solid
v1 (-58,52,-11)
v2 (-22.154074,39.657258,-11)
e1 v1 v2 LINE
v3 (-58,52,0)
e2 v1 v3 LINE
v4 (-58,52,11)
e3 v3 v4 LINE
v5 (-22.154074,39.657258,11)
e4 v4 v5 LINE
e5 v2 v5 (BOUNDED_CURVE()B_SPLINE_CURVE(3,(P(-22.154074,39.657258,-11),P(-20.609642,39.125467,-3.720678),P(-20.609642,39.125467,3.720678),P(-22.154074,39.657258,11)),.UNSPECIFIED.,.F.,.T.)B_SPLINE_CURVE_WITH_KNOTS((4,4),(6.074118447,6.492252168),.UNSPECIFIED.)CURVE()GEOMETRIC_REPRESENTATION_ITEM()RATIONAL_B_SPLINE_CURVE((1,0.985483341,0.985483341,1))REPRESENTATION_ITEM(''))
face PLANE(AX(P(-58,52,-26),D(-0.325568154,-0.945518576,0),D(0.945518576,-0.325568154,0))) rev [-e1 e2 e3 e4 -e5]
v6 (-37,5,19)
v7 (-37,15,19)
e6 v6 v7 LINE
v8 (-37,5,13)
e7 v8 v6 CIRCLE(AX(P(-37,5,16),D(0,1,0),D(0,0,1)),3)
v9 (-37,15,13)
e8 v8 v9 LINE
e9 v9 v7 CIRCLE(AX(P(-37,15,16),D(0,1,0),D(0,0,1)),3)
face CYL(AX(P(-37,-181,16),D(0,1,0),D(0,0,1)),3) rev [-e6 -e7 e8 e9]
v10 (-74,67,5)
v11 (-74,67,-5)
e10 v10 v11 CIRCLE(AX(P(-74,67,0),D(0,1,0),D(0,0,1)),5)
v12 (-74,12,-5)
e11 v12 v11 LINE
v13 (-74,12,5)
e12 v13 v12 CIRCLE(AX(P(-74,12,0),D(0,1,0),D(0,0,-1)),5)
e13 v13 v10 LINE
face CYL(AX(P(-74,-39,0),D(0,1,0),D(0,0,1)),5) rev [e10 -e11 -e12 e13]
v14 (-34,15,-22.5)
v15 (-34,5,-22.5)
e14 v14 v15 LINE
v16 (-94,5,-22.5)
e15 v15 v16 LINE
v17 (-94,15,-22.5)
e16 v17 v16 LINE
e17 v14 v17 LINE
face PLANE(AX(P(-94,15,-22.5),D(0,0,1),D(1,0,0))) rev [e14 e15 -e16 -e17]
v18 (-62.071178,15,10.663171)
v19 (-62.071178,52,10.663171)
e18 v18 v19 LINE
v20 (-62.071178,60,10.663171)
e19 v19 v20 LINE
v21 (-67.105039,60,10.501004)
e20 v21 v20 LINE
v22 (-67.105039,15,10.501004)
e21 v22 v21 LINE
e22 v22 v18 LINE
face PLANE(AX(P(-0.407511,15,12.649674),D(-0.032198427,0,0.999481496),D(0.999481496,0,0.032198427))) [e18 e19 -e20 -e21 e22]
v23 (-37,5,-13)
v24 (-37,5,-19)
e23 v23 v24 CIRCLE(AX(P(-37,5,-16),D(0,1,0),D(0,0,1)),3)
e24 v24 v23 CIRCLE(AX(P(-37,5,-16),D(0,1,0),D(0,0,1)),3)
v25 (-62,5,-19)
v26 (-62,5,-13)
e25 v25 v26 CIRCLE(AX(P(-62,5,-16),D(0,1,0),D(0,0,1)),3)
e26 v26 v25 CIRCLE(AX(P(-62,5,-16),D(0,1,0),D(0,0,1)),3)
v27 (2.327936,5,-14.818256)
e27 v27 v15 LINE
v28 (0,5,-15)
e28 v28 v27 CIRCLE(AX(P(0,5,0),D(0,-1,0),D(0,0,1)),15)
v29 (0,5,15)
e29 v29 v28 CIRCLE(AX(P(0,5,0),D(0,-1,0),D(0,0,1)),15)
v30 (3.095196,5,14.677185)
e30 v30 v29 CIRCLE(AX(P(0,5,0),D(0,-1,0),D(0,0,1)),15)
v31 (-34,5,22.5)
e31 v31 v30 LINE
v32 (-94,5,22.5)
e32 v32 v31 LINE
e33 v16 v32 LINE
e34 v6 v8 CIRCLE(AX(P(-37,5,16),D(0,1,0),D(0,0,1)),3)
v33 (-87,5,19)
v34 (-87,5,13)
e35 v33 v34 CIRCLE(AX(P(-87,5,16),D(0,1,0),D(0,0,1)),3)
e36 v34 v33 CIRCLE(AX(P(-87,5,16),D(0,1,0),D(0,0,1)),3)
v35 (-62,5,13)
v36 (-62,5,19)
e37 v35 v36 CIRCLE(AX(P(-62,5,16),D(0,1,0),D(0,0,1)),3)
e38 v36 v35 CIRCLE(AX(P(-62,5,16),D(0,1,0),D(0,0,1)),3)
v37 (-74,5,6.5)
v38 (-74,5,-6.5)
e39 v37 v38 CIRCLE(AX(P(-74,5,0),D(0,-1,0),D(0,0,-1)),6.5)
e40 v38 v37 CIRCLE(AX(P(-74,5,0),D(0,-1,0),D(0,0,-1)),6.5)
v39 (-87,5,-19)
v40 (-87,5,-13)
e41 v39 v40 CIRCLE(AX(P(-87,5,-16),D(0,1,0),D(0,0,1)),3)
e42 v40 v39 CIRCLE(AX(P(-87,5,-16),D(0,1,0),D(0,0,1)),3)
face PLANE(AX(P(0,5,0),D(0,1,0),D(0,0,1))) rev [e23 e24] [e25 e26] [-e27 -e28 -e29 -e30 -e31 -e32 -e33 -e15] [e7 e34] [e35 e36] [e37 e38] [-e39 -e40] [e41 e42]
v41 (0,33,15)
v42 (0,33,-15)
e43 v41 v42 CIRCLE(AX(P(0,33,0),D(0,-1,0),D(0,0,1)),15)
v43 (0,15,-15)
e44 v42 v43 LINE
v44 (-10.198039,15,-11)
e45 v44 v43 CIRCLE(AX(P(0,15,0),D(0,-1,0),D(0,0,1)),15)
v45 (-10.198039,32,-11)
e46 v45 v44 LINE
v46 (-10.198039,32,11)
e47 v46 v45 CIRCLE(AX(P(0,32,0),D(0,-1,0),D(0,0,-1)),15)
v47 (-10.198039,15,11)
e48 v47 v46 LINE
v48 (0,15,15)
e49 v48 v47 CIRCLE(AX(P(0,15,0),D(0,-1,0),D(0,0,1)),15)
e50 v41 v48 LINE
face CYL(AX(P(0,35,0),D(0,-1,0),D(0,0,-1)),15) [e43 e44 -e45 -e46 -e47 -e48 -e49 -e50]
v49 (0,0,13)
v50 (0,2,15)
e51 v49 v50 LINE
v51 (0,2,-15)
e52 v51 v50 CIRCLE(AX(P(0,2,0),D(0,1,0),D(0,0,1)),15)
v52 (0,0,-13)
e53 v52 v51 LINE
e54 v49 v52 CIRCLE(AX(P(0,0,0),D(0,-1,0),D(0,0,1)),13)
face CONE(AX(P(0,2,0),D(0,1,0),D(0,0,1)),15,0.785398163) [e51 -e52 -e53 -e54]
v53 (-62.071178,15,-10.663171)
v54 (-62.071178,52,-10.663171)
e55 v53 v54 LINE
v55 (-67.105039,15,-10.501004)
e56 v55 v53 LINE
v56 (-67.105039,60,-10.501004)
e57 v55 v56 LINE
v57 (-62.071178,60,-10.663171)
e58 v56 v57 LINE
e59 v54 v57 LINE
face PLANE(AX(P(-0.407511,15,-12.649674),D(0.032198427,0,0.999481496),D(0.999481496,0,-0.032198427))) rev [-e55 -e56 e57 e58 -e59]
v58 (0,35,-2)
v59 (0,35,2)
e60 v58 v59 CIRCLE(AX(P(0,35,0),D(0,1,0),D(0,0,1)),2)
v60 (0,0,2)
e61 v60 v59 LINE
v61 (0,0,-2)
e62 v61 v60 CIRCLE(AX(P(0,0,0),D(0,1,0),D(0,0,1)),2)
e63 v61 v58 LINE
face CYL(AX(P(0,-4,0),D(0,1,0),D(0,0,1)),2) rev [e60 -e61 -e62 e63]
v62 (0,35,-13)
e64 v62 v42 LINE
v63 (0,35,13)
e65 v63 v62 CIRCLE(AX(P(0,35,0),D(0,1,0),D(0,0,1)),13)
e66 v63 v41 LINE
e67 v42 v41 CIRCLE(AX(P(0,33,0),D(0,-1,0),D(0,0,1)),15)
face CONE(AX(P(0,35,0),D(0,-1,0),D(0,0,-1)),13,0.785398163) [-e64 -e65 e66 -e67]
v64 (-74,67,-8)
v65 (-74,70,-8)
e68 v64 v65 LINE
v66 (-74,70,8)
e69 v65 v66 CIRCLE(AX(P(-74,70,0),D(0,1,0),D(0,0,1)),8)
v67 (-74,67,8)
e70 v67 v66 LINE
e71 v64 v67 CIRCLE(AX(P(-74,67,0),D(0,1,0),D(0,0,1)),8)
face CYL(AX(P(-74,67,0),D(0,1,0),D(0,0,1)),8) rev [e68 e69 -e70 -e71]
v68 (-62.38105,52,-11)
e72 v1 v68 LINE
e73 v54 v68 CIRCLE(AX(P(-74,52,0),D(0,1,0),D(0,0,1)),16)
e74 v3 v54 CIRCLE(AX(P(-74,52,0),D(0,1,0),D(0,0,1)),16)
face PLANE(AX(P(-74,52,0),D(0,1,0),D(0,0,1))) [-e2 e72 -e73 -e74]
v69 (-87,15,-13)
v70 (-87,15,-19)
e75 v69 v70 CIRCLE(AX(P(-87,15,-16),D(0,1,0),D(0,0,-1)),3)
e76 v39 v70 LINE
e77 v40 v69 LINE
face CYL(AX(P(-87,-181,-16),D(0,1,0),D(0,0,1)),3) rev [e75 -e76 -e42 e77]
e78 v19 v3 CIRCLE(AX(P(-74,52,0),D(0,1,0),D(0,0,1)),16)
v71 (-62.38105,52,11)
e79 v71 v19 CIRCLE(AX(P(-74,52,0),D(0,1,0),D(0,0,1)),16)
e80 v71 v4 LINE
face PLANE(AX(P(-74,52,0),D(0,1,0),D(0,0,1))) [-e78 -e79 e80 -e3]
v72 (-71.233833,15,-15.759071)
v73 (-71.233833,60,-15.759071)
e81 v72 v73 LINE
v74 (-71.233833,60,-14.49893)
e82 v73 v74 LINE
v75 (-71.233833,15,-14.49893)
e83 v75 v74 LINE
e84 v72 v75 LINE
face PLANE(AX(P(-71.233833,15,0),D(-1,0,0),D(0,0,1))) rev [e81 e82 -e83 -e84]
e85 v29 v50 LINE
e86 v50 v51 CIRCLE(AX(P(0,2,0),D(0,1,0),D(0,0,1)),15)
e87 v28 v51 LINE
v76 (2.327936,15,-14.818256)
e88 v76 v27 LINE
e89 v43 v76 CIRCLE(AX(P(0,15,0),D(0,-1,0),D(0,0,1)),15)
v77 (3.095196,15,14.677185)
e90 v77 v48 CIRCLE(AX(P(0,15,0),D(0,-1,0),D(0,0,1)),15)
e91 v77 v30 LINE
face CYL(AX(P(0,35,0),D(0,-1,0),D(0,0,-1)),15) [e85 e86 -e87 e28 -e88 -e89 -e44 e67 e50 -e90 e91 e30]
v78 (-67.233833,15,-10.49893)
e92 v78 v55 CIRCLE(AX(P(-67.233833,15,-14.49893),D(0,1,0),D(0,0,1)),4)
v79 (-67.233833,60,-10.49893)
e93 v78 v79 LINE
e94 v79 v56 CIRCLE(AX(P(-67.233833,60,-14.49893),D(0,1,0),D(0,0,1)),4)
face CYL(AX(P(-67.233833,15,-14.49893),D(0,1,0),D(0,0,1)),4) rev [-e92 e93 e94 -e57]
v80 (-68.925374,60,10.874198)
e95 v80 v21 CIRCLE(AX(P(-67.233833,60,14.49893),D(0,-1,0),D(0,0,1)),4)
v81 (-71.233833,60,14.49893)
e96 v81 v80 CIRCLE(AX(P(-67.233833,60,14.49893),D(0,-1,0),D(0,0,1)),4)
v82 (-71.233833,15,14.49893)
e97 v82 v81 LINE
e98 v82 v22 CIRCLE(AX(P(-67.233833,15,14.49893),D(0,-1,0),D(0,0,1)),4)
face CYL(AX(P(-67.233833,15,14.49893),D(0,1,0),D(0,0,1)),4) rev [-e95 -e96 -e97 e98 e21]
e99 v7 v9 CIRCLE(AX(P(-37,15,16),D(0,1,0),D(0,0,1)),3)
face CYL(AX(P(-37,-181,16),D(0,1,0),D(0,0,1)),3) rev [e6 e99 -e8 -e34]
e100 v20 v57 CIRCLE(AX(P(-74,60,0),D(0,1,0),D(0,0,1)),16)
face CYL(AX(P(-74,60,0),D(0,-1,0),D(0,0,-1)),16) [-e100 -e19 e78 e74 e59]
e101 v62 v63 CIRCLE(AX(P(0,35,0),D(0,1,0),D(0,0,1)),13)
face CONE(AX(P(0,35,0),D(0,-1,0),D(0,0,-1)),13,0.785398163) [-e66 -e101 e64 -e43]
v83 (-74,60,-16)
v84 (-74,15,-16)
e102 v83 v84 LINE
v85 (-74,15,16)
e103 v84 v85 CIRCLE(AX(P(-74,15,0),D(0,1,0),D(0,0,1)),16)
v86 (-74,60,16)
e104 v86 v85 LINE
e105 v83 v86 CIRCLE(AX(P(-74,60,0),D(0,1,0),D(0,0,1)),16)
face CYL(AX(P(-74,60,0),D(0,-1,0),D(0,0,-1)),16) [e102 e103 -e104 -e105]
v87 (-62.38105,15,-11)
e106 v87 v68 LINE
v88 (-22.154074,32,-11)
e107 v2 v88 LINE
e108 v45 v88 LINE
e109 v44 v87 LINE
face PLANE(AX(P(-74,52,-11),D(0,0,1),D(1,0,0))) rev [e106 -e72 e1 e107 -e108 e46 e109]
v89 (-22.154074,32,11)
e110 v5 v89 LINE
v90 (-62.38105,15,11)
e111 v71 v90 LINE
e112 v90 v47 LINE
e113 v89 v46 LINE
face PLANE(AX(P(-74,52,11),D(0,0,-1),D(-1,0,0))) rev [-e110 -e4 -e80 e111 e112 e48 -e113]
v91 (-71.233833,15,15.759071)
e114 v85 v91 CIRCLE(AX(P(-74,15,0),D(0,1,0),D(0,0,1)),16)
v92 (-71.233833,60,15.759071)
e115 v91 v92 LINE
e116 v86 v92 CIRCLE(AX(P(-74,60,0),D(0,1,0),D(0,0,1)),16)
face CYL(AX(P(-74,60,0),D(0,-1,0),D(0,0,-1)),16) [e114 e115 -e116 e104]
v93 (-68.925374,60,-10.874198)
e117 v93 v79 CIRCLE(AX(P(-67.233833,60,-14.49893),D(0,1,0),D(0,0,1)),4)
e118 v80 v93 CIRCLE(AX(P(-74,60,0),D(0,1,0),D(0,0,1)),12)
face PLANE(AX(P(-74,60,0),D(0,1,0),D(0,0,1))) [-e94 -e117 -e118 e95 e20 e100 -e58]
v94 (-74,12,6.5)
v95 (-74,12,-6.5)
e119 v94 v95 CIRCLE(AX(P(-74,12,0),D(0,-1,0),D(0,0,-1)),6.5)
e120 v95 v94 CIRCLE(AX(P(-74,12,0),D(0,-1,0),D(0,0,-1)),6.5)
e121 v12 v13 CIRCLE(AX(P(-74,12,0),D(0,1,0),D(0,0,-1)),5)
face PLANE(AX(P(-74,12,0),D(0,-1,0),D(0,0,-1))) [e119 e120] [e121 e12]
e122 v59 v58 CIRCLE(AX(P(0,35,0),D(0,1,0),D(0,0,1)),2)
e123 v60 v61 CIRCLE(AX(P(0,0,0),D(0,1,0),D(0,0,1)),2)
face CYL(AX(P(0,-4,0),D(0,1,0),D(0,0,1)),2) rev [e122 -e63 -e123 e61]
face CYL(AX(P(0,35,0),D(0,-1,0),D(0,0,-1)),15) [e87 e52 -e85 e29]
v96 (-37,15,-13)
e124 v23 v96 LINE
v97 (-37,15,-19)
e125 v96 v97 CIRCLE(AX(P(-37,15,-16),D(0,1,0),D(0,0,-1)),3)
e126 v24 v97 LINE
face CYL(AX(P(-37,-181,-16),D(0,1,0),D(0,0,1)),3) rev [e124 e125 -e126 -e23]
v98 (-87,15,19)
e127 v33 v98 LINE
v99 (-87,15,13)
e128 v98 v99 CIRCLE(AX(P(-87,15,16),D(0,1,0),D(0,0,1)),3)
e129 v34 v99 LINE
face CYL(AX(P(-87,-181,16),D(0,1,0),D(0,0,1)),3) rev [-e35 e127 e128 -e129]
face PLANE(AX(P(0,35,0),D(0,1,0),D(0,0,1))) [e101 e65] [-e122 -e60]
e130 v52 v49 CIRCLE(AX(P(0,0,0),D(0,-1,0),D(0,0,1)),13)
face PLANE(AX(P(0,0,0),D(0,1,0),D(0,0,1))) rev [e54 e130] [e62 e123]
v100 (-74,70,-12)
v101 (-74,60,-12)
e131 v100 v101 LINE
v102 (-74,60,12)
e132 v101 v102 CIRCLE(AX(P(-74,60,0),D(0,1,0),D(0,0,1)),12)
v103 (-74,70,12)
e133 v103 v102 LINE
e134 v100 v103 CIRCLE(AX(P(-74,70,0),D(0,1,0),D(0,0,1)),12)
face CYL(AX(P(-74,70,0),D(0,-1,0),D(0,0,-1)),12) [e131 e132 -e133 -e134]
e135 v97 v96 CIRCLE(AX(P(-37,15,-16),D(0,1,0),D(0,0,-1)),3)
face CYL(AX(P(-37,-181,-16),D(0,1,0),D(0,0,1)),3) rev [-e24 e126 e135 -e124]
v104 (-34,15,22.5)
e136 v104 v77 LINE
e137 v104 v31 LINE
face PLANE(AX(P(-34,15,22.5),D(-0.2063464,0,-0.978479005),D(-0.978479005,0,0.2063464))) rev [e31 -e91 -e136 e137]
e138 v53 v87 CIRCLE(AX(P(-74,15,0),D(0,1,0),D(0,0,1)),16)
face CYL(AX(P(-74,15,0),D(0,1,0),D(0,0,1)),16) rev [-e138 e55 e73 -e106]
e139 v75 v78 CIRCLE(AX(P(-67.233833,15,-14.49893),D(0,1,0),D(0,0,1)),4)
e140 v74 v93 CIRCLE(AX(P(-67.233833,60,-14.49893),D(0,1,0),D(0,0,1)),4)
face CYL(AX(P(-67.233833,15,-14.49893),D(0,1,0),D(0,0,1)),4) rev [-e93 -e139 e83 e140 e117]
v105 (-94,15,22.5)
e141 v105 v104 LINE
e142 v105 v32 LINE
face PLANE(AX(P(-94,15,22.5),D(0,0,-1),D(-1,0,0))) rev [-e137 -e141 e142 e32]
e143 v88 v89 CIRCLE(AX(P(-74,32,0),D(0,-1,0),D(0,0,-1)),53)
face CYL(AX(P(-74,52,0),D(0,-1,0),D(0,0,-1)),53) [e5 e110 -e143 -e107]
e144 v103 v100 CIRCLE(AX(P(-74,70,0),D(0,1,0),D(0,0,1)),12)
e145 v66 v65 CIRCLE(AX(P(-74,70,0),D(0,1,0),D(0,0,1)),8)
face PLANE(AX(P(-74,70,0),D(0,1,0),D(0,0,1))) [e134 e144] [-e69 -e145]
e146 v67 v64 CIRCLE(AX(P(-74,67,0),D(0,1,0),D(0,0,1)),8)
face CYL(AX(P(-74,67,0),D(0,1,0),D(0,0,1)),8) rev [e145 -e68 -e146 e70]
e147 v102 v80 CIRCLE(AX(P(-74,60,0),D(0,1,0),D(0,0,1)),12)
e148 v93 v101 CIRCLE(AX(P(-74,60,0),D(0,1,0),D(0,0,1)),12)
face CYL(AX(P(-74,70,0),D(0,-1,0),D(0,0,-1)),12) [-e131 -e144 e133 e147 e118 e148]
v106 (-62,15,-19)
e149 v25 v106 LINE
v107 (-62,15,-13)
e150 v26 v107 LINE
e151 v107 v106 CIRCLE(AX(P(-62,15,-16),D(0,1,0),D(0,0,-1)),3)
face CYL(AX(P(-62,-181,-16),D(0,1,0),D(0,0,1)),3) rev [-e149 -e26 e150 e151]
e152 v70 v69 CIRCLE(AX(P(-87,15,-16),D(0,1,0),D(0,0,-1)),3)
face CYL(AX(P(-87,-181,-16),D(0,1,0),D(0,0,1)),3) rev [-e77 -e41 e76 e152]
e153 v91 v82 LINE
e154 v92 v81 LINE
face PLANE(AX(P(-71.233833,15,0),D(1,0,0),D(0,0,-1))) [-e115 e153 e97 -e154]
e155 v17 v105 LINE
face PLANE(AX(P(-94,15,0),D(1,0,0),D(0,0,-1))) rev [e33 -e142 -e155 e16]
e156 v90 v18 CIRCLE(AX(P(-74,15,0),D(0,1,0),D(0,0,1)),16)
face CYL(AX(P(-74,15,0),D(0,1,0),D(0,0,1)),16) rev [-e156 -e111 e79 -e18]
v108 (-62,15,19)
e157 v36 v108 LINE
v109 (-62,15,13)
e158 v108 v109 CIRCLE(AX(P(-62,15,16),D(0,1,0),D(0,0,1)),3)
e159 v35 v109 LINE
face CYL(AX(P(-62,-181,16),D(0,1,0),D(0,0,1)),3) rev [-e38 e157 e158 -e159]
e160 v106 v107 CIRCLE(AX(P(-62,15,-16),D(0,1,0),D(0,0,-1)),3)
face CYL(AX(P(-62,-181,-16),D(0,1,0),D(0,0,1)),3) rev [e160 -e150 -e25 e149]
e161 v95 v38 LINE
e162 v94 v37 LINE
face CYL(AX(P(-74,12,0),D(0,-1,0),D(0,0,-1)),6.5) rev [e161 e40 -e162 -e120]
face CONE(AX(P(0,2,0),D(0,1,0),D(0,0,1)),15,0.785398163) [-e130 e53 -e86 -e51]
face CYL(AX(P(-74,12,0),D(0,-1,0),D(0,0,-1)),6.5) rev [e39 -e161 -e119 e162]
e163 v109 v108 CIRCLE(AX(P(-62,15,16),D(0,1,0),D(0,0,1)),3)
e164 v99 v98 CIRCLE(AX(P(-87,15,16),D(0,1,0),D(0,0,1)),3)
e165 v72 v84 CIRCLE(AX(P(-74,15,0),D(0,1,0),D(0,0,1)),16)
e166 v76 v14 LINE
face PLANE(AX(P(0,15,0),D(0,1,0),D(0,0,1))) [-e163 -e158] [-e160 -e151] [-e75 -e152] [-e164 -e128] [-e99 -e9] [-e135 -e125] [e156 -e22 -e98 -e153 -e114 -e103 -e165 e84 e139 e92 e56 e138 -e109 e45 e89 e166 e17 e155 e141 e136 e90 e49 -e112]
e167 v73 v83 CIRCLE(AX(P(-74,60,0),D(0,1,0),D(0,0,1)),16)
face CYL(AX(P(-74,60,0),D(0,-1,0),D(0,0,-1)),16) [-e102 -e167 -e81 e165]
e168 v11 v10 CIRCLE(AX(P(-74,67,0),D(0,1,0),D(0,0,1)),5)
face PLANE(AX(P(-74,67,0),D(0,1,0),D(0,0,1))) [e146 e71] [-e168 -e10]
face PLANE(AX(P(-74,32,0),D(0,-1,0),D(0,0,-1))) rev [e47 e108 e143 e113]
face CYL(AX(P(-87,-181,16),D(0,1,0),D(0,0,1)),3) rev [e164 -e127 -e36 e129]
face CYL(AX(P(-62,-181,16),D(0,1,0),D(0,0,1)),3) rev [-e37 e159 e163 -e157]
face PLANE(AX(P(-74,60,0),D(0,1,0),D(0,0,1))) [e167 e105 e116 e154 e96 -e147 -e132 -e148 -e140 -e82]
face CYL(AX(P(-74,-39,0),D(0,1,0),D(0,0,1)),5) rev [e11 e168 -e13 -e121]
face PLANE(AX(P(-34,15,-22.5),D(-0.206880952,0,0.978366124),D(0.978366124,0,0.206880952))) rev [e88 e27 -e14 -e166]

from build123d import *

# Parameters (mm, degrees)
PIVOT_HUB_SKETCH_R           = 15
PIVOT_HUB_30_DEPTH           = 35
BASE_PLATE_DEPTH             = 10
COLUMN_SKETCH_R              = 16
COLUMN_32_DEPTH              = 45
SLOPED_WEB_DEPTH             = 37
WEB_TRIM_CUT_DEPTH           = 37
WEB_PAD_DEPTH                = 17
HUB_CHAMFER_A_SIZE           = 2
HUB_CHAMFER_B_SIZE           = 2
HUB_PIN_HOLE_SKETCH_R        = 2
HUB_PIN_HOLE_4_DEPTH         = 39
COLUMN_TOP_BOSS_SKETCH_R     = 12
COLUMN_TOP_BOSS_24_DEPTH     = 10
TOP_COUNTERBORE_SKETCH_R     = 8
TOP_COUNTERBORE_16_DEPTH     = 3
COLUMN_BORE_SKETCH_R         = 5
COLUMN_BORE_10_DEPTH         = 106
BOTTOM_COUNTERBORE_SKETCH_R  = 6.5
BOTTOM_COUNTERBORE_13_DEPTH  = 7
COLUMN_START                 = -45
COLUMN_SLOT_DEPTH            = 45
BASE_MOUNTING_HOLES_SKETCH_R = 3
BASE_MOUNTING_HOLES_6_DEPTH  = 196


with BuildPart() as part:
    # Pivot Hub Sketch → Pivot Hub Ø30 (new body)
    with BuildSketch(Plane(origin=(0, 0, 0), x_dir=(1, 0, 0), z_dir=(0, 1, 0))):
        with Locations(Location((0, 0, 0), (0, 0, 270))):
            Circle(PIVOT_HUB_SKETCH_R)
    extrude(amount=PIVOT_HUB_30_DEPTH)

    # Base Plate Sketch → Base Plate (add)
    with BuildSketch(Plane(origin=(0, 5, 0), x_dir=(1, 0, 0), z_dir=(0, 1, 0))):
        with BuildLine():
            Line((-94, 0), (-94, 22.5))
            Line((-94, 22.5), (-34, 22.5))
            Line((-34, 22.5), (2.327936287, 14.81825606))
            ThreePointArc((2.327936287, 14.81825606), (-14.994927572, -0.390060375), (3.095195933, -14.677185089))
            Line((3.095195933, -14.677185089), (-34, -22.5))
            Line((-34, -22.5), (-94, -22.5))
            Line((-94, -22.5), (-94, 0))
        make_face()
    extrude(amount=BASE_PLATE_DEPTH)

    # Column Sketch → Column Ø32 (add)
    with BuildSketch(Plane(origin=(0, 15, 0), x_dir=(1, 0, 0), z_dir=(0, 1, 0))):
        with Locations(Location((-74, 0, 0), (0, 0, 90))):
            Circle(COLUMN_SKETCH_R)
    extrude(amount=COLUMN_32_DEPTH)

    # Web Sketch → Sloped Web (add)
    with BuildSketch(Plane(origin=(0, 15, 0), x_dir=(1, 0, 0), z_dir=(0, 1, 0))):
        with BuildLine():
            Line((-74, 11), (-22.154074413, 11))
            ThreePointArc((-22.154074413, 11), (-21, 0), (-22.154074413, -11))
            Line((-22.154074413, -11), (-74, -11))
            ThreePointArc((-74, -11), (-85, 0), (-74, 11))
        make_face()
    extrude(amount=SLOPED_WEB_DEPTH)

    # Web Trim Sketch → Web Trim Cut (cut)
    with BuildSketch(Plane.XY.offset(11)):
        Polygon((-58, 52), (-22.154074413, 52), (-16.501763131, 52), (-16.501763131, 37.711011143), align=None)
    extrude(amount=-WEB_TRIM_CUT_DEPTH, mode=Mode.SUBTRACT)

    # Web Pad Sketch → Web Pad (add)
    with BuildSketch(Plane(origin=(0, 15, 0), x_dir=(1, 0, 0), z_dir=(0, 1, 0))):
        with BuildLine():
            Line((-22.154074413, 11), (-1.869546507, 11))
            Line((-1.869546507, 11), (-1.869546507, -11))
            Line((-1.869546507, -11), (-22.154074413, -11))
            ThreePointArc((-22.154074413, -11), (-21, 0), (-22.154074413, 11))
        make_face()
    extrude(amount=WEB_PAD_DEPTH)

    # Hub Chamfer A
    hub_chamfer_a_edges = [part.edges().sort_by_distance(p)[0] for p in [
        (0, 35, -15),
    ]]
    chamfer(hub_chamfer_a_edges, length=HUB_CHAMFER_A_SIZE)

    # Hub Chamfer B
    hub_chamfer_b_edges = [part.edges().sort_by_distance(p)[0] for p in [
        (0, 0, -15),
    ]]
    chamfer(hub_chamfer_b_edges, length=HUB_CHAMFER_B_SIZE)

    # Hub Pin Hole Sketch → Hub Pin Hole Ø4 (cut)
    with BuildSketch(Plane(origin=(0, 35, 0), x_dir=(1, 0, 0), z_dir=(0, 1, 0))):
        with Locations(Location((0, 0, 0), (0, 0, 270))):
            Circle(HUB_PIN_HOLE_SKETCH_R)
    extrude(amount=-HUB_PIN_HOLE_4_DEPTH, mode=Mode.SUBTRACT)

    # Column Top Boss Sketch → Column Top Boss Ø24 (add)
    with BuildSketch(Plane(origin=(0, 60, 0), x_dir=(1, 0, 0), z_dir=(0, 1, 0))):
        with Locations(Location((-74, 0, 0), (0, 0, 270))):
            Circle(COLUMN_TOP_BOSS_SKETCH_R)
    extrude(amount=COLUMN_TOP_BOSS_24_DEPTH)

    # Top Counterbore Sketch → Top Counterbore Ø16 (cut)
    with BuildSketch(Plane(origin=(0, 70, 0), x_dir=(1, 0, 0), z_dir=(0, 1, 0))):
        with Locations(Location((-74, 0, 0), (0, 0, 270))):
            Circle(TOP_COUNTERBORE_SKETCH_R)
    extrude(amount=-TOP_COUNTERBORE_16_DEPTH, mode=Mode.SUBTRACT)

    # Column Bore Sketch → Column Bore Ø10 (cut)
    with BuildSketch(Plane(origin=(0, 67, 0), x_dir=(1, 0, 0), z_dir=(0, 1, 0))):
        with Locations(Location((-74, 0, 0), (0, 0, 270))):
            Circle(COLUMN_BORE_SKETCH_R)
    extrude(amount=-COLUMN_BORE_10_DEPTH, mode=Mode.SUBTRACT)

    # Bottom Counterbore Sketch → Bottom Counterbore Ø13 (cut)
    with BuildSketch(Plane.XZ.offset(-5)):
        with Locations(Location((-74, 0, 0), (0, 0, 270))):
            Circle(BOTTOM_COUNTERBORE_SKETCH_R)
    extrude(amount=-BOTTOM_COUNTERBORE_13_DEPTH, mode=Mode.SUBTRACT)

    # Column Slot Sketch → Column Slot (cut)
    with BuildSketch(Plane(origin=(0, 60, 0), x_dir=(1, 0, 0), z_dir=(0, 1, 0)).offset(COLUMN_START)):
        with BuildLine():
            ThreePointArc((-62.071178187, 10.663170736), (-66.223257294, 13.982927908), (-71.233832555, 15.759070965))
            Line((-71.233832555, 15.759070965), (-71.233832555, 14.49893024))
            ThreePointArc((-71.233832555, 14.49893024), (-70.680112836, 12.468375582), (-69.172256444, 11))
            ThreePointArc((-69.172256444, 11), (-69.049905074, 10.934960458), (-68.925374416, 10.87419768))
            ThreePointArc((-68.925374416, 10.87419768), (-68.037177922, 10.580431009), (-67.105038845, 10.501004255))
            Line((-67.105038845, 10.501004255), (-62.071178187, 10.663170736))
        make_face()
        with BuildLine():
            Line((-62.071178187, -10.663170736), (-67.105038845, -10.501004255))
            ThreePointArc((-67.105038845, -10.501004255), (-70.016351662, -11.62532842), (-71.233832555, -14.49893024))
            Line((-71.233832555, -14.49893024), (-71.233832555, -15.759070965))
            ThreePointArc((-71.233832555, -15.759070965), (-66.223257294, -13.982927908), (-62.071178187, -10.663170736))
        make_face()
    extrude(amount=COLUMN_SLOT_DEPTH, mode=Mode.SUBTRACT)

    # Base Mounting Holes Sketch → Base Mounting Holes Ø6 (cut)
    with BuildSketch(Plane(origin=(0, 15, 0), x_dir=(1, 0, 0), z_dir=(0, 1, 0))):
        with Locations(Location((-87, -16, 0), (0, 0, 270))):
            Circle(BASE_MOUNTING_HOLES_SKETCH_R)
        with Locations(Location((-62, -16, 0), (0, 0, 270))):
            Circle(BASE_MOUNTING_HOLES_SKETCH_R)
        with Locations(Location((-37, -16, 0), (0, 0, 270))):
            Circle(BASE_MOUNTING_HOLES_SKETCH_R)
        with Locations(Location((-87, 16, 0), (0, 0, 270))):
            Circle(BASE_MOUNTING_HOLES_SKETCH_R)
        with Locations(Location((-37, 16, 0), (0, 0, 270))):
            Circle(BASE_MOUNTING_HOLES_SKETCH_R)
        with Locations(Location((-62, 16, 0), (0, 0, 270))):
            Circle(BASE_MOUNTING_HOLES_SKETCH_R)
    extrude(amount=-BASE_MOUNTING_HOLES_6_DEPTH, mode=Mode.SUBTRACT)


solid = part.part
